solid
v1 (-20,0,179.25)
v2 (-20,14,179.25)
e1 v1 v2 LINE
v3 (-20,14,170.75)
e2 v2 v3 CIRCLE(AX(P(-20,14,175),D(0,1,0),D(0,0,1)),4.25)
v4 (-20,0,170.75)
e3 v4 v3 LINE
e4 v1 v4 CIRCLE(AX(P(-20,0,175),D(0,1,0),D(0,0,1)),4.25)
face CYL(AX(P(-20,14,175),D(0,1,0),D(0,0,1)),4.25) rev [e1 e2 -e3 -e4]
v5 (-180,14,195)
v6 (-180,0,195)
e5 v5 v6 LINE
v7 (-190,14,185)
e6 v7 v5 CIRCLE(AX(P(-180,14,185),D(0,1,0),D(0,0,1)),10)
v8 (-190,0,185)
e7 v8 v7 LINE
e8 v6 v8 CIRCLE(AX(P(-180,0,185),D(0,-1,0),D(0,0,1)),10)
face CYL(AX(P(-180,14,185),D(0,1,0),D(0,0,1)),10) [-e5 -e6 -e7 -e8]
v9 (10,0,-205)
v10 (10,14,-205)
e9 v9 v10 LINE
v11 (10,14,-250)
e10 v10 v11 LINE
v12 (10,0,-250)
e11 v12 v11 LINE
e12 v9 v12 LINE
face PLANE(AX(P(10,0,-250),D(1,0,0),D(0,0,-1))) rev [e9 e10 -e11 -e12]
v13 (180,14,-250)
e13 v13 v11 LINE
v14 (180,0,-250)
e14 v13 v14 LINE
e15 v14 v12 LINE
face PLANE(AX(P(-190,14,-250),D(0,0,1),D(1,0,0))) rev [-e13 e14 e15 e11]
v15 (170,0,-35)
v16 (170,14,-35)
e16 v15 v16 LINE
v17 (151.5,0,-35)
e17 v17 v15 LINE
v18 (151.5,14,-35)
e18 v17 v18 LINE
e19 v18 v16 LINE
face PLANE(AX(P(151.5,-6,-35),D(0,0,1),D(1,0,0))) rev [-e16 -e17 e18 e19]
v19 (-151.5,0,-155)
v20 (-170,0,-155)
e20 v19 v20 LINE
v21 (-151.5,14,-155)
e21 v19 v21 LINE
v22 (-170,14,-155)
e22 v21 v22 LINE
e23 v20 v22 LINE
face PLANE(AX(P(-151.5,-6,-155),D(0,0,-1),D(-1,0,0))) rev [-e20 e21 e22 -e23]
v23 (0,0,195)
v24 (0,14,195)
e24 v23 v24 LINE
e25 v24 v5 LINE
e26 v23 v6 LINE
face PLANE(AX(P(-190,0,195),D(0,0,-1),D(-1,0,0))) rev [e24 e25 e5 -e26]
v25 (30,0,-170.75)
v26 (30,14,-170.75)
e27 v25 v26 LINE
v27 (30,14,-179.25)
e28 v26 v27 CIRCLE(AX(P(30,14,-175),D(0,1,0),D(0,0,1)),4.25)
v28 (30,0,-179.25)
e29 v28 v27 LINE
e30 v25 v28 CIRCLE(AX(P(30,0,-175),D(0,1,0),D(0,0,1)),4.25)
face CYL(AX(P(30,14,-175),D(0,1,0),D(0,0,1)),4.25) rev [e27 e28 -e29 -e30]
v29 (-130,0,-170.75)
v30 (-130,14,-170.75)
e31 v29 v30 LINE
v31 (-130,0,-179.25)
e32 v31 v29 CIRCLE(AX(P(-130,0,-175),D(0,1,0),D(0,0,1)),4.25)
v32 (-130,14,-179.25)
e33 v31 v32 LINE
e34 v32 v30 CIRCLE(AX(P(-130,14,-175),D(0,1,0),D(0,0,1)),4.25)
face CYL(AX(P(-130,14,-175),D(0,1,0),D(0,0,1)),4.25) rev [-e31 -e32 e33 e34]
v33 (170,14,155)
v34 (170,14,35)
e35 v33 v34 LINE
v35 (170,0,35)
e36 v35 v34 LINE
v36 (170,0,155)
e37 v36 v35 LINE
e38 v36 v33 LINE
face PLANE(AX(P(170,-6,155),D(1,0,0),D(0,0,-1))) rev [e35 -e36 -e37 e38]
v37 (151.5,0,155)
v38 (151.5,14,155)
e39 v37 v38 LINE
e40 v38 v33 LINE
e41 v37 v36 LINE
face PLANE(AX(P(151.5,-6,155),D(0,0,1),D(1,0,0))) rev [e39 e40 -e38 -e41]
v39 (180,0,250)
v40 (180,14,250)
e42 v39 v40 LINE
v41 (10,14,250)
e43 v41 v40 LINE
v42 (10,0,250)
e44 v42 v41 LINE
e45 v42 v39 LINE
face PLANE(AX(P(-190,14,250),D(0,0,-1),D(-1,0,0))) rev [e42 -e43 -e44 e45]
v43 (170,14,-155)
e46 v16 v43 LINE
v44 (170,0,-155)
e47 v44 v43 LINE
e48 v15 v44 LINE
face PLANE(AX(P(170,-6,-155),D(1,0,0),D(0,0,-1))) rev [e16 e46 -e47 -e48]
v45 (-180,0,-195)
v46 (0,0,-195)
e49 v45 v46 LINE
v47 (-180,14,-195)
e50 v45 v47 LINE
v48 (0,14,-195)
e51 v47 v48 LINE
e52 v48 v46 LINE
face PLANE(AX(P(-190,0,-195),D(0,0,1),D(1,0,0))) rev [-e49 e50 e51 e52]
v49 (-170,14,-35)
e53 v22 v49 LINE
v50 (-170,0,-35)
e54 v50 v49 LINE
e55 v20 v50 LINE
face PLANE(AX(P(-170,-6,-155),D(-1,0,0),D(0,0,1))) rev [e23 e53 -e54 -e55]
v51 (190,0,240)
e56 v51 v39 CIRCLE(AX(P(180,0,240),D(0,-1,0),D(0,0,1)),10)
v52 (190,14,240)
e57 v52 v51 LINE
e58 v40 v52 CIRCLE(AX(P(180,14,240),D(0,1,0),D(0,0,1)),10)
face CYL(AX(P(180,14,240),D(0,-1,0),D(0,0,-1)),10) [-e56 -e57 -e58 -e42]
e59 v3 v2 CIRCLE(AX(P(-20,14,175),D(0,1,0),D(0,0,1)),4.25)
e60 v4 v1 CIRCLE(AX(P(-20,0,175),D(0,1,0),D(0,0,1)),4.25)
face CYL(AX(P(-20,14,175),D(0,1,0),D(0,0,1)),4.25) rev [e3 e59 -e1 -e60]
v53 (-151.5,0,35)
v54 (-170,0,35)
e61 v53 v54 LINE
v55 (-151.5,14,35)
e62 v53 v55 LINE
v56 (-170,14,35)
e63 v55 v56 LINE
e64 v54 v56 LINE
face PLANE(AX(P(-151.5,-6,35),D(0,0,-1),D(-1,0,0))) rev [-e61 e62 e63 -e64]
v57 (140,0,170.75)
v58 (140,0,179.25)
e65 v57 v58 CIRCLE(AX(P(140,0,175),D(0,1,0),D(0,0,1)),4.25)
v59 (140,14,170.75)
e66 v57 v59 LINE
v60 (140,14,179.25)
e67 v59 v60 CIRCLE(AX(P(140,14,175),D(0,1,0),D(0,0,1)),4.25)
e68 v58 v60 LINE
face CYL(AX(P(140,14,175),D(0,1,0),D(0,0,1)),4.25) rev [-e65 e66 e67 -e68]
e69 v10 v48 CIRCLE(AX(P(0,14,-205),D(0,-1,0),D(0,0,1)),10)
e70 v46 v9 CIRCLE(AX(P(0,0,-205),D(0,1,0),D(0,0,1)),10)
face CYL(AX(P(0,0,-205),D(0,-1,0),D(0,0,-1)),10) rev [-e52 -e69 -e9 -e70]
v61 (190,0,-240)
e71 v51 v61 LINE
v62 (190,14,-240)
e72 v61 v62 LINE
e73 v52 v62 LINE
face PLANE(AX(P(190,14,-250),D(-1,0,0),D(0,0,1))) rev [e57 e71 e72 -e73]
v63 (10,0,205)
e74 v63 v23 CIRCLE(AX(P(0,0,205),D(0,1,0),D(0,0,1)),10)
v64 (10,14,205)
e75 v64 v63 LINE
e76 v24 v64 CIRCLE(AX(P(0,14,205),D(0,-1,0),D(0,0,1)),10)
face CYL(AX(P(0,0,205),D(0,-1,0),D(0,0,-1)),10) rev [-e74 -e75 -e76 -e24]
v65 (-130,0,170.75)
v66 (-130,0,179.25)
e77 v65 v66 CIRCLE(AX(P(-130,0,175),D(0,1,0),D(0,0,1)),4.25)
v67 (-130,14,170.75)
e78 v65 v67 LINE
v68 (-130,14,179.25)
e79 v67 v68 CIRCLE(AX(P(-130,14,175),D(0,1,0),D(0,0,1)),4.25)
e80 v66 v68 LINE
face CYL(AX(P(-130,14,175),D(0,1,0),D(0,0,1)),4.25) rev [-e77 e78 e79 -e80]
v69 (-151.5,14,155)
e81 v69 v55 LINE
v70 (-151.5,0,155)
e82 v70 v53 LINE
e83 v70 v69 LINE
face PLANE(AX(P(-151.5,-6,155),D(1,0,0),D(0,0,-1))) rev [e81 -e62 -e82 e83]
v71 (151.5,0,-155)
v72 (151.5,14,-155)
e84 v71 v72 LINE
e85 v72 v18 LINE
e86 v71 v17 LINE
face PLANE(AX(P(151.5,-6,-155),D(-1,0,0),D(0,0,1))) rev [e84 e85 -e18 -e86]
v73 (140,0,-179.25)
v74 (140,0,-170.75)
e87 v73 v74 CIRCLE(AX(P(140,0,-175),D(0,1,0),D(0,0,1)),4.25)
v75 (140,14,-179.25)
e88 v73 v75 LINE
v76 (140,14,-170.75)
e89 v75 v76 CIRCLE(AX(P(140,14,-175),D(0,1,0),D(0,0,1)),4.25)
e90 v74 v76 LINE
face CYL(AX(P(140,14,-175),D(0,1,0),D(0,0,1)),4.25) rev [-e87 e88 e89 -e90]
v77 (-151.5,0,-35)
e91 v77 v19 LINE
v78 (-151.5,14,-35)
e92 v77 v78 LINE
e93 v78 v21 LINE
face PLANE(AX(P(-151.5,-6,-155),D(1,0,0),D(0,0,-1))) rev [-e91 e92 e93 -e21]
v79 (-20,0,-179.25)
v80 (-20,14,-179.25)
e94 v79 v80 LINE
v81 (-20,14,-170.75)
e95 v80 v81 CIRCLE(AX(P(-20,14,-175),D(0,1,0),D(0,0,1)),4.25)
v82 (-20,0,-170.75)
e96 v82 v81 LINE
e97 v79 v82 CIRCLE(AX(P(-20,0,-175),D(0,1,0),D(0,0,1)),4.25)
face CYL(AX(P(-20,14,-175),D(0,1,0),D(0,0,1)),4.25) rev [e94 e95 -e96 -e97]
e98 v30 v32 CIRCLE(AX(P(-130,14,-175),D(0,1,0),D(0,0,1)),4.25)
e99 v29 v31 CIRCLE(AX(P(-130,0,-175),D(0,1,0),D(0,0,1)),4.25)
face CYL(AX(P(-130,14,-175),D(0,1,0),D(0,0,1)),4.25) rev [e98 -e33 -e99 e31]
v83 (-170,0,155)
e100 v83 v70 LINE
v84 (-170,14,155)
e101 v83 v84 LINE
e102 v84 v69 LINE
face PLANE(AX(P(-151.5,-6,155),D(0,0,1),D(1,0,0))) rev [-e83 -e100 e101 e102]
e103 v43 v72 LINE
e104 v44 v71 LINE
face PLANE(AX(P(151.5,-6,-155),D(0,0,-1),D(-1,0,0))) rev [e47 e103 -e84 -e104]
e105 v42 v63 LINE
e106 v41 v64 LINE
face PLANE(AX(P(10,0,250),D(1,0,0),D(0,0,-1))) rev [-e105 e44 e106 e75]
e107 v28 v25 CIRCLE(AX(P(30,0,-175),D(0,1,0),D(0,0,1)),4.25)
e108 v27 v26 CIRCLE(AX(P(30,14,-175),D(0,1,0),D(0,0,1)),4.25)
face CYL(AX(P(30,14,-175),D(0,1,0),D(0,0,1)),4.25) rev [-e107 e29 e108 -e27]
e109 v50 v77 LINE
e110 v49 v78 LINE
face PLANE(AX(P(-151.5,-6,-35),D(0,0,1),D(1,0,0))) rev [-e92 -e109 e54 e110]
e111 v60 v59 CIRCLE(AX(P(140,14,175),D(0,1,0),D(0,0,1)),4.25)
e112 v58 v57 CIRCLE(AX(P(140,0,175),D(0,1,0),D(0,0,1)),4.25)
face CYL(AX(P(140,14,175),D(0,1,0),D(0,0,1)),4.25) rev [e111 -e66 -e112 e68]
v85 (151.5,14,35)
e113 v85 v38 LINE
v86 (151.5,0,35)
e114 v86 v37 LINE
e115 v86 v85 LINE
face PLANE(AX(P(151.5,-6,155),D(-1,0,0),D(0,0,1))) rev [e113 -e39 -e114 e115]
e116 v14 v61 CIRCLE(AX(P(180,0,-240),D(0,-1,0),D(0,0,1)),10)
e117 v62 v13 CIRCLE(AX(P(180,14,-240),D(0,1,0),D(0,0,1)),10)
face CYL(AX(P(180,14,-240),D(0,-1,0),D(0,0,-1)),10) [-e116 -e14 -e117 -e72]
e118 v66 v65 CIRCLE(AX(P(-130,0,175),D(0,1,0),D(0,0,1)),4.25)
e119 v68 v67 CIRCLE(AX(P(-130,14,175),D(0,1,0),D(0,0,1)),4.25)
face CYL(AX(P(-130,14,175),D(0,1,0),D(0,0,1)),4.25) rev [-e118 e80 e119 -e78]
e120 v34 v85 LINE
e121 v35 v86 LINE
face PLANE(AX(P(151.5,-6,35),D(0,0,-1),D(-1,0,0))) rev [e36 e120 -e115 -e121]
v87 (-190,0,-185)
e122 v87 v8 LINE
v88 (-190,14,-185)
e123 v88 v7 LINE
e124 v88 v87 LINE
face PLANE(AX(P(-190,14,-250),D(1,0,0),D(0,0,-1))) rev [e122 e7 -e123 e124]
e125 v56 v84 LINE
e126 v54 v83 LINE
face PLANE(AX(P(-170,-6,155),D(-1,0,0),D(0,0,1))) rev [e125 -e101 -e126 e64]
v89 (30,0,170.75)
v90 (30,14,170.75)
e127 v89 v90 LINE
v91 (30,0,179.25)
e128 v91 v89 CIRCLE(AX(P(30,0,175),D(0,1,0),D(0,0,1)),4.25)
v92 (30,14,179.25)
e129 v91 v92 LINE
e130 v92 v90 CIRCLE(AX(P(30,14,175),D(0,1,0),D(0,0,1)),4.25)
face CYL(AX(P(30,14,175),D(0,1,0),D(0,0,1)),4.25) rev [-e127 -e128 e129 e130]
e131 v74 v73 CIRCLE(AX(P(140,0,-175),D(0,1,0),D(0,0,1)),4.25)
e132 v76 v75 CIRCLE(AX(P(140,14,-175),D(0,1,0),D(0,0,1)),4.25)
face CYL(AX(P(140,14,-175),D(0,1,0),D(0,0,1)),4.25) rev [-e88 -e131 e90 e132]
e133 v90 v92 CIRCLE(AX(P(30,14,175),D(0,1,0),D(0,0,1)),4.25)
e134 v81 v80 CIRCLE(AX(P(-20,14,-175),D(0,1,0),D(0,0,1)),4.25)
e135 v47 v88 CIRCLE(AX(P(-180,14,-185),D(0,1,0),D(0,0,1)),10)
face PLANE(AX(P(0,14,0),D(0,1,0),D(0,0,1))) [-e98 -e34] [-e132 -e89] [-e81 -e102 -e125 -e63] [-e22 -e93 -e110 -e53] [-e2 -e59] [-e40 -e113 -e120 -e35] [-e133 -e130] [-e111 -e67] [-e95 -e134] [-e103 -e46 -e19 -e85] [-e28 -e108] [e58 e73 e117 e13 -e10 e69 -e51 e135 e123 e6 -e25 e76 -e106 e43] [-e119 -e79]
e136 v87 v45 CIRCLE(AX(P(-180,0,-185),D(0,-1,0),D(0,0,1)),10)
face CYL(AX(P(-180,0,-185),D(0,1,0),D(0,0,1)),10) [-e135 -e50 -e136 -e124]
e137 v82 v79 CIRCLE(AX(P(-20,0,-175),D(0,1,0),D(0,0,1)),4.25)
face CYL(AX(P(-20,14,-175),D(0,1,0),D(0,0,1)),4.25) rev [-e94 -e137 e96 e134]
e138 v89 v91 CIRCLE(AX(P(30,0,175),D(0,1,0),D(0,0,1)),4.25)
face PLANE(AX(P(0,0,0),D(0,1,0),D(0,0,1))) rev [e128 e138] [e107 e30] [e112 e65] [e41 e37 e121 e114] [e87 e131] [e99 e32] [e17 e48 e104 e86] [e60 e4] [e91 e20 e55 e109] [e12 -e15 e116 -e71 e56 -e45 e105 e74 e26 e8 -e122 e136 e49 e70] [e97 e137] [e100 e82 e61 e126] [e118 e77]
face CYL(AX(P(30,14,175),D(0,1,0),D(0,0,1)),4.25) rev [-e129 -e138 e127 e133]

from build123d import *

# Parameters (mm, degrees)
SKETCH1_W                   = 380
SKETCH1_H                   = 500
BOSS_EXTRUDE1_DEPTH         = 14
SKETCH2_W                   = 200
SKETCH2_H                   = 55
CUT_EXTRUDE1_DEPTH          = 14
FILLET1_R                   = 10
SKETCH3_W                   = 18.5
SKETCH3_H                   = 120
CUT_EXTRUDE2_DEPTH          = 20
M10_TAPPED_HOLE1_AT_2_COUNT = 2
M10_TAPPED_HOLE1_AT_2_PITCH = 110
M10_TAPPED_HOLE1_AT_3_COUNT = 2
M10_TAPPED_HOLE1_AT_3_PITCH = 366.878726557
M10_TAPPED_HOLE1_AT_4_COUNT = 2
M10_TAPPED_HOLE1_AT_4_PITCH = 350
LPATTERN1_COUNT             = 2
LPATTERN1_PITCH             = 160
FILLET2_R                   = 10


with BuildPart() as part:
    # Sketch1 → Boss-Extrude1 (new body)
    with BuildSketch(Plane(origin=(0, 0, 0), x_dir=(1, 0, 0), z_dir=(0, 1, 0))):
        Rectangle(SKETCH1_W, SKETCH1_H)
    extrude(amount=BOSS_EXTRUDE1_DEPTH)

    # Sketch2 → Cut-Extrude1 (cut)
    with BuildSketch(Plane(origin=(0, 14, 0), x_dir=(1, 0, 0), z_dir=(0, 1, 0))):
        with Locations((-90, 222.5)):
            Rectangle(SKETCH2_W, SKETCH2_H)
        with Locations((-90, -222.5)):
            Rectangle(SKETCH2_W, SKETCH2_H)
    extrude(amount=-CUT_EXTRUDE1_DEPTH, mode=Mode.SUBTRACT)

    # Fillet1
    fillet1_edges = [part.edges().sort_by_distance(p)[0] for p in [
        (10, 7, -195),
        (10, 7, 195),
    ]]
    fillet(fillet1_edges, radius=FILLET1_R)

    # Sketch3 → Cut-Extrude2 (cut)
    with BuildSketch(Plane(origin=(0, 14, 0), x_dir=(1, 0, 0), z_dir=(0, 1, 0))):
        with Locations((160.75, 95)):
            Rectangle(SKETCH3_W, SKETCH3_H)
        with Locations((160.75, -95)):
            Rectangle(SKETCH3_W, SKETCH3_H)
        with Locations((-160.75, -95)):
            Rectangle(SKETCH3_W, SKETCH3_H)
        with Locations((-160.75, 95)):
            Rectangle(SKETCH3_W, SKETCH3_H)
    extrude(amount=-CUT_EXTRUDE2_DEPTH, mode=Mode.SUBTRACT)

    # Sketch5 → M10 Tapped Hole1 (revolve, cut)
    with BuildSketch(Plane(origin=(30, 14, 175), x_dir=(0, 0, 1), z_dir=(1, 0, 0))):
        Polygon((0, 0), (0, 55.553657631), (4.25, 53), (4.25, 0), align=None)
    m10_tapped_hole1 = revolve(axis=Axis((30, 20.35, 175), (0, -1, 0)), mode=Mode.SUBTRACT)

    # M10 Tapped Hole1 at 2: M10 Tapped Hole1 ×2
    with Locations(*[(i * M10_TAPPED_HOLE1_AT_2_PITCH, 0, 0) for i in range(1, M10_TAPPED_HOLE1_AT_2_COUNT)]):
        add(m10_tapped_hole1, mode=Mode.SUBTRACT)

    # M10 Tapped Hole1 at 3: M10 Tapped Hole1 ×2
    with Locations(*[Vector(0.29982659674039447, 0, -0.9539937169012556) * (i * M10_TAPPED_HOLE1_AT_3_PITCH) for i in range(1, M10_TAPPED_HOLE1_AT_3_COUNT)]):
        add(m10_tapped_hole1, mode=Mode.SUBTRACT)

    # M10 Tapped Hole1 at 4: M10 Tapped Hole1 ×2
    with Locations(*[(0, 0, -i * M10_TAPPED_HOLE1_AT_4_PITCH) for i in range(1, M10_TAPPED_HOLE1_AT_4_COUNT)]):
        add(m10_tapped_hole1, mode=Mode.SUBTRACT)

    # LPattern1: M10 Tapped Hole1 ×2
    with Locations(*[(-i * LPATTERN1_PITCH, 0, 0) for i in range(1, LPATTERN1_COUNT)]):
        add(m10_tapped_hole1, mode=Mode.SUBTRACT)

    # LPattern1 copy 1 sketch → LPattern1 copy 1 (revolve, cut)
    with BuildSketch(Plane(origin=(-20, 14, 175), x_dir=(0, 0, 1), z_dir=(1, 0, 0))):
        Polygon((0, 0), (0, 55.553657631), (4.25, 53), (4.25, 0), align=None)
    revolve(axis=Axis((-20, 20.35, 175), (0, -1, 0)), mode=Mode.SUBTRACT)

    # LPattern1 copy 2 sketch → LPattern1 copy 2 (revolve, cut)
    with BuildSketch(Plane(origin=(-20, 14, -175), x_dir=(0, 0, 1), z_dir=(1, 0, 0))):
        Polygon((0, 0), (0, 55.553657631), (4.25, 53), (4.25, 0), align=None)
    revolve(axis=Axis((-20, 20.35, -175), (0, -1, 0)), mode=Mode.SUBTRACT)

    # LPattern1 copy 3 sketch → LPattern1 copy 3 (revolve, cut)
    with BuildSketch(Plane(origin=(-130, 14, -175), x_dir=(0, 0, 1), z_dir=(1, 0, 0))):
        Polygon((0, 0), (0, 55.553657631), (4.25, 53), (4.25, 0), align=None)
    revolve(axis=Axis((-130, 20.35, -175), (0, -1, 0)), mode=Mode.SUBTRACT)

    # Fillet2
    fillet2_edges = [part.edges().sort_by_distance(p)[0] for p in [
        (-190, 7, -195),
        (-190, 7, 195),
        (190, 7, 250),
        (190, 7, -250),
    ]]
    fillet(fillet2_edges, radius=FILLET2_R)


solid = part.part
